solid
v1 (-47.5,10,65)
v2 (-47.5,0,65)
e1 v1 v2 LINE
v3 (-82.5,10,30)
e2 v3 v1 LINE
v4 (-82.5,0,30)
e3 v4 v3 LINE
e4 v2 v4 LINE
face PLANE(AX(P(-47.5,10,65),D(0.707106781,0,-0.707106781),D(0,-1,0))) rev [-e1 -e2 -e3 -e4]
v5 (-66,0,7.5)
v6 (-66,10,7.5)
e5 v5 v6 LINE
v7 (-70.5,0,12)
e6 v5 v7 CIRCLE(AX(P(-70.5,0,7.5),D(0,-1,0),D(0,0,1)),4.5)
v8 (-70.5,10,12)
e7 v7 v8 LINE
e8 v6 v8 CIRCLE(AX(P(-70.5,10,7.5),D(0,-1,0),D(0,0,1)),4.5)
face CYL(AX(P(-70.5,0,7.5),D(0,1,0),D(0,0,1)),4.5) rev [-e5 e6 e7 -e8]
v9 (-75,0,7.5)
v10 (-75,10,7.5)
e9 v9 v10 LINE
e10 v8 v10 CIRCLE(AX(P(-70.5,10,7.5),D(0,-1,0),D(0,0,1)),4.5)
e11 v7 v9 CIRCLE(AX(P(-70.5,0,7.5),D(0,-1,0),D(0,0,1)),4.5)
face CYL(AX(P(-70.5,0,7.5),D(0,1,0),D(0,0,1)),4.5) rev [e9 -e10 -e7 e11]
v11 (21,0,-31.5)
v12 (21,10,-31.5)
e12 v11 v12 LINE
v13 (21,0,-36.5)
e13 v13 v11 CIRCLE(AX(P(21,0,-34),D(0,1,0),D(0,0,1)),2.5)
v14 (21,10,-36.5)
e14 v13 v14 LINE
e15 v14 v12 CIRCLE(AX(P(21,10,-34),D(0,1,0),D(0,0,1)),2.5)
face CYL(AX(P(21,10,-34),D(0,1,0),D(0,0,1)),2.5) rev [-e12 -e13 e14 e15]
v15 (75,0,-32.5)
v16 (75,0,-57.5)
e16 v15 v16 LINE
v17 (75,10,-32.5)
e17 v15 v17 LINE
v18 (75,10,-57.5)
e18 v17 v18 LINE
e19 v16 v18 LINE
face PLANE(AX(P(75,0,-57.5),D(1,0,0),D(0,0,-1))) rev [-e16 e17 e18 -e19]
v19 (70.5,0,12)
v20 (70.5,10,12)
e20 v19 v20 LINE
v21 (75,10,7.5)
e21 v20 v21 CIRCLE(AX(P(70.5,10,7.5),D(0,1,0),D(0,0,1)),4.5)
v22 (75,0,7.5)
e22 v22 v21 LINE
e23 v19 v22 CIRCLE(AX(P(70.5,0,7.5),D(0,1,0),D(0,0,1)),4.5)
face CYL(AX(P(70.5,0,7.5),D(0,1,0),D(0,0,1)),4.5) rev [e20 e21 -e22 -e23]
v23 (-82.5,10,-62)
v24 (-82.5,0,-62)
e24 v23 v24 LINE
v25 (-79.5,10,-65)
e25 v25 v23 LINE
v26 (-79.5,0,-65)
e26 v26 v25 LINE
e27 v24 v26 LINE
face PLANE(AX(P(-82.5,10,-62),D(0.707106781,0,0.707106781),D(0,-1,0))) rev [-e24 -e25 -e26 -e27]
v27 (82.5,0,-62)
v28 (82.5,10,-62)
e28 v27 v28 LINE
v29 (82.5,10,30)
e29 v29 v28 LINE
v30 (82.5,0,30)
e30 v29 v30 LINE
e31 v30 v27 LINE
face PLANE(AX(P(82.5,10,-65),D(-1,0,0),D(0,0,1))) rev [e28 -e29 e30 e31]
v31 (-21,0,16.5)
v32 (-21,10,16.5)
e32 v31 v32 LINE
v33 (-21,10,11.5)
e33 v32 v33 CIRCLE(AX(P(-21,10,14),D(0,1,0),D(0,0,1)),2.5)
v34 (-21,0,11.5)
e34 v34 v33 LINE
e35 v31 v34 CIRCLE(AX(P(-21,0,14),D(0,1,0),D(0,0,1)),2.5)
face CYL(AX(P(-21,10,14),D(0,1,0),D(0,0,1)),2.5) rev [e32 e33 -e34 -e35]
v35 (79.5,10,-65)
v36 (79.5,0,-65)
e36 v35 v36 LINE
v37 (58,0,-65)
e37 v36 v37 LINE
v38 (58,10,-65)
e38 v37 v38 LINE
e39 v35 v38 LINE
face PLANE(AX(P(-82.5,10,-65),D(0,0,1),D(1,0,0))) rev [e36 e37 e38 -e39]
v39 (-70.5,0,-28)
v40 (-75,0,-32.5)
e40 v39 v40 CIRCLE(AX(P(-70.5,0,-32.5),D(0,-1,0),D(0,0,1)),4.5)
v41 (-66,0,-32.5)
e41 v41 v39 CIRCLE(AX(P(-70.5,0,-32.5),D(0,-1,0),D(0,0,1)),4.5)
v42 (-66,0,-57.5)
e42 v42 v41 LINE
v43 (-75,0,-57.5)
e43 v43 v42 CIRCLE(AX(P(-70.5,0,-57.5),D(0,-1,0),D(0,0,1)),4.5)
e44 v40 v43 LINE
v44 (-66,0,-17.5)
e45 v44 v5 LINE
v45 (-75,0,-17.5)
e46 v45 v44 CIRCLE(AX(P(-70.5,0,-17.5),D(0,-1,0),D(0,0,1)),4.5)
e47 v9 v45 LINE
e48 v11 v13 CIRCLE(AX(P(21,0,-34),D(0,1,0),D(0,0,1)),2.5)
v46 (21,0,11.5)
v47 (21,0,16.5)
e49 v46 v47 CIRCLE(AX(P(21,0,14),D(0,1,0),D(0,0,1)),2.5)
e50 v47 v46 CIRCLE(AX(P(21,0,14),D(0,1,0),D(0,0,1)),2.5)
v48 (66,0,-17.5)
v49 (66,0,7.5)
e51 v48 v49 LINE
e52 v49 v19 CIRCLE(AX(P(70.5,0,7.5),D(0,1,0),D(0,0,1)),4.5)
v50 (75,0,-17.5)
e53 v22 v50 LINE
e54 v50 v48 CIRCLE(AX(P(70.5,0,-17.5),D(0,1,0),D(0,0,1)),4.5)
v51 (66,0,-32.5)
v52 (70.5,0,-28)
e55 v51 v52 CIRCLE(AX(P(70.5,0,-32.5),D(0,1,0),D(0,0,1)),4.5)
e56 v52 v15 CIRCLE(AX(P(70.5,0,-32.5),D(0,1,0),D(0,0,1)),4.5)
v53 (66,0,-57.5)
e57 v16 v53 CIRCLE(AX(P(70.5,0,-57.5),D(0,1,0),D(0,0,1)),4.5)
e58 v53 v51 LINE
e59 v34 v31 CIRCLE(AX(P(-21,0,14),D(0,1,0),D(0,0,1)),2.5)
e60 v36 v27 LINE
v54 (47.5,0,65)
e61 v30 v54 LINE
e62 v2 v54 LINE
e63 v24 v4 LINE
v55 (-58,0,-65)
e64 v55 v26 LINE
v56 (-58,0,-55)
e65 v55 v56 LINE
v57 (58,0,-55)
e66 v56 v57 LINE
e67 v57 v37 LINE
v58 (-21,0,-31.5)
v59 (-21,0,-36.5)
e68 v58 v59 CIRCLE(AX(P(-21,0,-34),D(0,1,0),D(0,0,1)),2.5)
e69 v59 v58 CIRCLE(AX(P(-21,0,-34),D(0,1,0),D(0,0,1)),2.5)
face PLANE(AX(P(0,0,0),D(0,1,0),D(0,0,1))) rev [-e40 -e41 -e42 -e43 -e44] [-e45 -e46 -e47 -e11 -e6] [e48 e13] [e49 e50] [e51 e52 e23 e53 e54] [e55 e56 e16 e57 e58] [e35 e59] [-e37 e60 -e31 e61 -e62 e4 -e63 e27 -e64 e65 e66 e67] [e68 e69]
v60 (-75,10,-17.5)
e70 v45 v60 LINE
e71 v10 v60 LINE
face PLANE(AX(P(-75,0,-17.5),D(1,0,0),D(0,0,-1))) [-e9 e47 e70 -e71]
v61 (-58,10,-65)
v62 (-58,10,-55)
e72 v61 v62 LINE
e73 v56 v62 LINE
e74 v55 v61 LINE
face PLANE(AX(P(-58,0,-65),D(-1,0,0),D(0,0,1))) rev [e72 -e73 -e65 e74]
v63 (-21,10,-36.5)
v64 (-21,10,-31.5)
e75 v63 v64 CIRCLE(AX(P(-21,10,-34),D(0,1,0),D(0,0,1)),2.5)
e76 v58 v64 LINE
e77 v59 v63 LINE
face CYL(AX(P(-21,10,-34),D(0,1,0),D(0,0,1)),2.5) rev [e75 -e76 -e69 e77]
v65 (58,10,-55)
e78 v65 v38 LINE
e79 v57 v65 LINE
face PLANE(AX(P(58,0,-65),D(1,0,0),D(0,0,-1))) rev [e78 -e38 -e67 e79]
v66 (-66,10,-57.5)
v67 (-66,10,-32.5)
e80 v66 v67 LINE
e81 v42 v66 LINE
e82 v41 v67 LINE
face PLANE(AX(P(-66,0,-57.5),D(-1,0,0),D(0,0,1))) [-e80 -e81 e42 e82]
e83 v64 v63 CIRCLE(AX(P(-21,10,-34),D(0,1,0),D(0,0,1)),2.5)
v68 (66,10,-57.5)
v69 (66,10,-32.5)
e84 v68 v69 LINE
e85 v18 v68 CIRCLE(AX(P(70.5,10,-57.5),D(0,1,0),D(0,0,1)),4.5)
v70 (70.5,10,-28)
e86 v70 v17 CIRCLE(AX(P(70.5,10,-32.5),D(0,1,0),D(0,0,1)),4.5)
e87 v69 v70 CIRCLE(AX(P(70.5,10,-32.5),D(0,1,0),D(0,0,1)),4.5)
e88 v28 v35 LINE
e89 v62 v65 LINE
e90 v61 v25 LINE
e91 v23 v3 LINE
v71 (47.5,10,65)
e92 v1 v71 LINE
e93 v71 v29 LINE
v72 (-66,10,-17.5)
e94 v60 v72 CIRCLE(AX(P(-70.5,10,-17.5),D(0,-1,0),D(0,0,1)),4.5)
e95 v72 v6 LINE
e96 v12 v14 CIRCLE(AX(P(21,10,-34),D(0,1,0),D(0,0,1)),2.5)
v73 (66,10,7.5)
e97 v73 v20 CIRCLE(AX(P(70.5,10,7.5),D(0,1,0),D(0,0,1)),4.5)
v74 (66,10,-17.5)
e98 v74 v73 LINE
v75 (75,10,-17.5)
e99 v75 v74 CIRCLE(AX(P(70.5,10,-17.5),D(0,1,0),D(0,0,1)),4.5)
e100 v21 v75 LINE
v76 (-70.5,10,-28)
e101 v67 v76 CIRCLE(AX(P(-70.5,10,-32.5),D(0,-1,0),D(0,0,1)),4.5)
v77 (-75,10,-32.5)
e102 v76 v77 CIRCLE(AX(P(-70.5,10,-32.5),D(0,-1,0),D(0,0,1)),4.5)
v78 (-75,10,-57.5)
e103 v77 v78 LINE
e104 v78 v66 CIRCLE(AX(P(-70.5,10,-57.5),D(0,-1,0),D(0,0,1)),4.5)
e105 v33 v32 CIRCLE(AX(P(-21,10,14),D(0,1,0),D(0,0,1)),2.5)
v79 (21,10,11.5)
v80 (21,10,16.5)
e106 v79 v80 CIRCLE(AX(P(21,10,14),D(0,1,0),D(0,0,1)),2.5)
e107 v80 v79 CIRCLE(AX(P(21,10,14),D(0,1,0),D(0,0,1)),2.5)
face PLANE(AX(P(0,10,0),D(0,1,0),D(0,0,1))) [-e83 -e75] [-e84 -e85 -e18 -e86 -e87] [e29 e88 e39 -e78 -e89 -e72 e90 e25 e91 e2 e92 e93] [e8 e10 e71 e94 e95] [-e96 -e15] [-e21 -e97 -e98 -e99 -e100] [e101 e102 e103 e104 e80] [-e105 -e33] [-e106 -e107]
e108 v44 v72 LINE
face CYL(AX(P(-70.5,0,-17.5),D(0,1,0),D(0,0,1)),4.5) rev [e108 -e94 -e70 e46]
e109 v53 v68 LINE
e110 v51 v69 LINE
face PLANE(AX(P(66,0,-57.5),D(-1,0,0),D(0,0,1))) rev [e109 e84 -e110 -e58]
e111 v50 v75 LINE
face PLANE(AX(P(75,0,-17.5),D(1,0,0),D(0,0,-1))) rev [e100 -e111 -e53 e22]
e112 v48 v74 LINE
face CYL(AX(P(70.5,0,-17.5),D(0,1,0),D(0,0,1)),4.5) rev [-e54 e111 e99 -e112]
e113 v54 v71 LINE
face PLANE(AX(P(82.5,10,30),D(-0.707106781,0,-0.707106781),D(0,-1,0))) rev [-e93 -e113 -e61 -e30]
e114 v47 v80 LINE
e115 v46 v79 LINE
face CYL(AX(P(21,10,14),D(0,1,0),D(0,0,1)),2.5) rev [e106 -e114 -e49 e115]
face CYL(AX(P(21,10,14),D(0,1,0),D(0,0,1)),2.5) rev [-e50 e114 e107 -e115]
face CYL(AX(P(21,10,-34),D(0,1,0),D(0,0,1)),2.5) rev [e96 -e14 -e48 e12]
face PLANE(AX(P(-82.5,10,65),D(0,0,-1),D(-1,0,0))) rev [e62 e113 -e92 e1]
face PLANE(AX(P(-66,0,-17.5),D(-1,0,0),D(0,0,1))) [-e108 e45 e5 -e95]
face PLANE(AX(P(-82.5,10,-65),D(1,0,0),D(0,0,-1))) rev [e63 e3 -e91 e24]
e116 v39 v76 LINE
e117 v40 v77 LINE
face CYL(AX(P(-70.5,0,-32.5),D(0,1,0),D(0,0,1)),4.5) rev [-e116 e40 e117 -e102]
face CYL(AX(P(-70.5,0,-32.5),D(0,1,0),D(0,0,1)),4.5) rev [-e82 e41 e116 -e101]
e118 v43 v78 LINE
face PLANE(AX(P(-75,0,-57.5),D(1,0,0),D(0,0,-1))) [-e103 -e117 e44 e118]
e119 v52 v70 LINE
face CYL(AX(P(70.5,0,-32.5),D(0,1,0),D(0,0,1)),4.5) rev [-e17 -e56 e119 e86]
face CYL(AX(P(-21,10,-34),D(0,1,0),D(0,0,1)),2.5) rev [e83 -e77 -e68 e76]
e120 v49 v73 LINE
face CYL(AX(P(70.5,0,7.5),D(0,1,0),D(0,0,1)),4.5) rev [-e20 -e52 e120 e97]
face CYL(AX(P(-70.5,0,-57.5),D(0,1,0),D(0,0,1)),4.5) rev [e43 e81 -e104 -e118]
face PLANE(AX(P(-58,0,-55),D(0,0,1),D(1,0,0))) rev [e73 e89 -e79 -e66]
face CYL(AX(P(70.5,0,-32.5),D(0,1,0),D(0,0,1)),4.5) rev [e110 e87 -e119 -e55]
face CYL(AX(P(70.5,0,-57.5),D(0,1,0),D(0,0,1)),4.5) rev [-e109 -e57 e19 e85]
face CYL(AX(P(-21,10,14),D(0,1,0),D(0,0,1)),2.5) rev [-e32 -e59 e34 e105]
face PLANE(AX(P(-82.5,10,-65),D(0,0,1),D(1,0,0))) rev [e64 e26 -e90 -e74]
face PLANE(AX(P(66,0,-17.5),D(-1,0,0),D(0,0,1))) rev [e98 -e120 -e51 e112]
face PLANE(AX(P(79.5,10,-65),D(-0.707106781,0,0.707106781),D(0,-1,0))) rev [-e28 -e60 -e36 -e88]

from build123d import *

# Parameters (mm, degrees)
SKETCH_2_W          = 165
SKETCH_2_H          = 130
EXTRUDE_1_DEPTH     = 10
SKETCH_3_W          = 116
SKETCH_3_H          = 10
CUT_EXTRUDE_1_DEPTH = 10
CUT_EXTRUDE_2_DEPTH = 106.50473923
CHAMFER_1_SIZE      = 35
HOLE_WIZARD_M6_1_D  = 5
CHAMFER_3_SIZE      = 3


with BuildPart() as part:
    # 草图2 → 凸台-拉伸1 (new body)
    with BuildSketch(Plane(origin=(0, 0, 0), x_dir=(1, 0, 0), z_dir=(0, 1, 0))):
        Rectangle(SKETCH_2_W, SKETCH_2_H)
    extrude(amount=EXTRUDE_1_DEPTH)

    # 草图3 → 切除-拉伸1 (cut)
    with BuildSketch(Plane(origin=(0, 10, 0), x_dir=(1, 0, 0), z_dir=(0, 1, 0))):
        with Locations((0, 60)):
            Rectangle(SKETCH_3_W, SKETCH_3_H)
    extrude(amount=-CUT_EXTRUDE_1_DEPTH, mode=Mode.SUBTRACT)

    # 草图4 → 切除-拉伸2 (cut, through all)
    with BuildSketch(Plane(origin=(0, 10, 0), x_dir=(1, 0, 0), z_dir=(0, 1, 0))):
        with BuildLine():
            Line((75, 57.5), (75, 32.5))
            ThreePointArc((75, 32.5), (70.5, 28), (66, 32.5))
            Line((66, 32.5), (66, 57.5))
            ThreePointArc((66, 57.5), (70.5, 62), (75, 57.5))
        make_face()
        with BuildLine():
            Line((75, 17.5), (75, -7.5))
            ThreePointArc((75, -7.5), (70.5, -12), (66, -7.5))
            Line((66, -7.5), (66, 17.5))
            ThreePointArc((66, 17.5), (70.5, 22), (75, 17.5))
        make_face()
    cut_extrude_2 = extrude(amount=-CUT_EXTRUDE_2_DEPTH, mode=Mode.SUBTRACT)

    # 倒角1
    chamfer_1_edges = [part.edges().sort_by_distance(p)[0] for p in [
        (82.5, 5, 65),
        (-82.5, 5, 65),
    ]]
    chamfer(chamfer_1_edges, length=CHAMFER_1_SIZE)

    # M6 螺纹孔1 (through all)
    with Locations(Plane(origin=(0, 10, 0), x_dir=(1, 0, 0), z_dir=(0, 1, 0))):
        with Locations((21, -14), (21, 34), (-21, 34), (-21, -14)):
            Hole(HOLE_WIZARD_M6_1_D / 2)

    # 倒角3
    chamfer_3_edges = [part.edges().sort_by_distance(p)[0] for p in [
        (-82.5, 5, -65),
        (82.5, 5, -65),
    ]]
    chamfer(chamfer_3_edges, length=CHAMFER_3_SIZE)

    # 镜向1: 切除-拉伸2 across plane
    add(cut_extrude_2.mirror(Plane(origin=(0, 0, 0), x_dir=(0, 0, 1), z_dir=(1, 0, 0))), mode=Mode.SUBTRACT)


solid = part.part
